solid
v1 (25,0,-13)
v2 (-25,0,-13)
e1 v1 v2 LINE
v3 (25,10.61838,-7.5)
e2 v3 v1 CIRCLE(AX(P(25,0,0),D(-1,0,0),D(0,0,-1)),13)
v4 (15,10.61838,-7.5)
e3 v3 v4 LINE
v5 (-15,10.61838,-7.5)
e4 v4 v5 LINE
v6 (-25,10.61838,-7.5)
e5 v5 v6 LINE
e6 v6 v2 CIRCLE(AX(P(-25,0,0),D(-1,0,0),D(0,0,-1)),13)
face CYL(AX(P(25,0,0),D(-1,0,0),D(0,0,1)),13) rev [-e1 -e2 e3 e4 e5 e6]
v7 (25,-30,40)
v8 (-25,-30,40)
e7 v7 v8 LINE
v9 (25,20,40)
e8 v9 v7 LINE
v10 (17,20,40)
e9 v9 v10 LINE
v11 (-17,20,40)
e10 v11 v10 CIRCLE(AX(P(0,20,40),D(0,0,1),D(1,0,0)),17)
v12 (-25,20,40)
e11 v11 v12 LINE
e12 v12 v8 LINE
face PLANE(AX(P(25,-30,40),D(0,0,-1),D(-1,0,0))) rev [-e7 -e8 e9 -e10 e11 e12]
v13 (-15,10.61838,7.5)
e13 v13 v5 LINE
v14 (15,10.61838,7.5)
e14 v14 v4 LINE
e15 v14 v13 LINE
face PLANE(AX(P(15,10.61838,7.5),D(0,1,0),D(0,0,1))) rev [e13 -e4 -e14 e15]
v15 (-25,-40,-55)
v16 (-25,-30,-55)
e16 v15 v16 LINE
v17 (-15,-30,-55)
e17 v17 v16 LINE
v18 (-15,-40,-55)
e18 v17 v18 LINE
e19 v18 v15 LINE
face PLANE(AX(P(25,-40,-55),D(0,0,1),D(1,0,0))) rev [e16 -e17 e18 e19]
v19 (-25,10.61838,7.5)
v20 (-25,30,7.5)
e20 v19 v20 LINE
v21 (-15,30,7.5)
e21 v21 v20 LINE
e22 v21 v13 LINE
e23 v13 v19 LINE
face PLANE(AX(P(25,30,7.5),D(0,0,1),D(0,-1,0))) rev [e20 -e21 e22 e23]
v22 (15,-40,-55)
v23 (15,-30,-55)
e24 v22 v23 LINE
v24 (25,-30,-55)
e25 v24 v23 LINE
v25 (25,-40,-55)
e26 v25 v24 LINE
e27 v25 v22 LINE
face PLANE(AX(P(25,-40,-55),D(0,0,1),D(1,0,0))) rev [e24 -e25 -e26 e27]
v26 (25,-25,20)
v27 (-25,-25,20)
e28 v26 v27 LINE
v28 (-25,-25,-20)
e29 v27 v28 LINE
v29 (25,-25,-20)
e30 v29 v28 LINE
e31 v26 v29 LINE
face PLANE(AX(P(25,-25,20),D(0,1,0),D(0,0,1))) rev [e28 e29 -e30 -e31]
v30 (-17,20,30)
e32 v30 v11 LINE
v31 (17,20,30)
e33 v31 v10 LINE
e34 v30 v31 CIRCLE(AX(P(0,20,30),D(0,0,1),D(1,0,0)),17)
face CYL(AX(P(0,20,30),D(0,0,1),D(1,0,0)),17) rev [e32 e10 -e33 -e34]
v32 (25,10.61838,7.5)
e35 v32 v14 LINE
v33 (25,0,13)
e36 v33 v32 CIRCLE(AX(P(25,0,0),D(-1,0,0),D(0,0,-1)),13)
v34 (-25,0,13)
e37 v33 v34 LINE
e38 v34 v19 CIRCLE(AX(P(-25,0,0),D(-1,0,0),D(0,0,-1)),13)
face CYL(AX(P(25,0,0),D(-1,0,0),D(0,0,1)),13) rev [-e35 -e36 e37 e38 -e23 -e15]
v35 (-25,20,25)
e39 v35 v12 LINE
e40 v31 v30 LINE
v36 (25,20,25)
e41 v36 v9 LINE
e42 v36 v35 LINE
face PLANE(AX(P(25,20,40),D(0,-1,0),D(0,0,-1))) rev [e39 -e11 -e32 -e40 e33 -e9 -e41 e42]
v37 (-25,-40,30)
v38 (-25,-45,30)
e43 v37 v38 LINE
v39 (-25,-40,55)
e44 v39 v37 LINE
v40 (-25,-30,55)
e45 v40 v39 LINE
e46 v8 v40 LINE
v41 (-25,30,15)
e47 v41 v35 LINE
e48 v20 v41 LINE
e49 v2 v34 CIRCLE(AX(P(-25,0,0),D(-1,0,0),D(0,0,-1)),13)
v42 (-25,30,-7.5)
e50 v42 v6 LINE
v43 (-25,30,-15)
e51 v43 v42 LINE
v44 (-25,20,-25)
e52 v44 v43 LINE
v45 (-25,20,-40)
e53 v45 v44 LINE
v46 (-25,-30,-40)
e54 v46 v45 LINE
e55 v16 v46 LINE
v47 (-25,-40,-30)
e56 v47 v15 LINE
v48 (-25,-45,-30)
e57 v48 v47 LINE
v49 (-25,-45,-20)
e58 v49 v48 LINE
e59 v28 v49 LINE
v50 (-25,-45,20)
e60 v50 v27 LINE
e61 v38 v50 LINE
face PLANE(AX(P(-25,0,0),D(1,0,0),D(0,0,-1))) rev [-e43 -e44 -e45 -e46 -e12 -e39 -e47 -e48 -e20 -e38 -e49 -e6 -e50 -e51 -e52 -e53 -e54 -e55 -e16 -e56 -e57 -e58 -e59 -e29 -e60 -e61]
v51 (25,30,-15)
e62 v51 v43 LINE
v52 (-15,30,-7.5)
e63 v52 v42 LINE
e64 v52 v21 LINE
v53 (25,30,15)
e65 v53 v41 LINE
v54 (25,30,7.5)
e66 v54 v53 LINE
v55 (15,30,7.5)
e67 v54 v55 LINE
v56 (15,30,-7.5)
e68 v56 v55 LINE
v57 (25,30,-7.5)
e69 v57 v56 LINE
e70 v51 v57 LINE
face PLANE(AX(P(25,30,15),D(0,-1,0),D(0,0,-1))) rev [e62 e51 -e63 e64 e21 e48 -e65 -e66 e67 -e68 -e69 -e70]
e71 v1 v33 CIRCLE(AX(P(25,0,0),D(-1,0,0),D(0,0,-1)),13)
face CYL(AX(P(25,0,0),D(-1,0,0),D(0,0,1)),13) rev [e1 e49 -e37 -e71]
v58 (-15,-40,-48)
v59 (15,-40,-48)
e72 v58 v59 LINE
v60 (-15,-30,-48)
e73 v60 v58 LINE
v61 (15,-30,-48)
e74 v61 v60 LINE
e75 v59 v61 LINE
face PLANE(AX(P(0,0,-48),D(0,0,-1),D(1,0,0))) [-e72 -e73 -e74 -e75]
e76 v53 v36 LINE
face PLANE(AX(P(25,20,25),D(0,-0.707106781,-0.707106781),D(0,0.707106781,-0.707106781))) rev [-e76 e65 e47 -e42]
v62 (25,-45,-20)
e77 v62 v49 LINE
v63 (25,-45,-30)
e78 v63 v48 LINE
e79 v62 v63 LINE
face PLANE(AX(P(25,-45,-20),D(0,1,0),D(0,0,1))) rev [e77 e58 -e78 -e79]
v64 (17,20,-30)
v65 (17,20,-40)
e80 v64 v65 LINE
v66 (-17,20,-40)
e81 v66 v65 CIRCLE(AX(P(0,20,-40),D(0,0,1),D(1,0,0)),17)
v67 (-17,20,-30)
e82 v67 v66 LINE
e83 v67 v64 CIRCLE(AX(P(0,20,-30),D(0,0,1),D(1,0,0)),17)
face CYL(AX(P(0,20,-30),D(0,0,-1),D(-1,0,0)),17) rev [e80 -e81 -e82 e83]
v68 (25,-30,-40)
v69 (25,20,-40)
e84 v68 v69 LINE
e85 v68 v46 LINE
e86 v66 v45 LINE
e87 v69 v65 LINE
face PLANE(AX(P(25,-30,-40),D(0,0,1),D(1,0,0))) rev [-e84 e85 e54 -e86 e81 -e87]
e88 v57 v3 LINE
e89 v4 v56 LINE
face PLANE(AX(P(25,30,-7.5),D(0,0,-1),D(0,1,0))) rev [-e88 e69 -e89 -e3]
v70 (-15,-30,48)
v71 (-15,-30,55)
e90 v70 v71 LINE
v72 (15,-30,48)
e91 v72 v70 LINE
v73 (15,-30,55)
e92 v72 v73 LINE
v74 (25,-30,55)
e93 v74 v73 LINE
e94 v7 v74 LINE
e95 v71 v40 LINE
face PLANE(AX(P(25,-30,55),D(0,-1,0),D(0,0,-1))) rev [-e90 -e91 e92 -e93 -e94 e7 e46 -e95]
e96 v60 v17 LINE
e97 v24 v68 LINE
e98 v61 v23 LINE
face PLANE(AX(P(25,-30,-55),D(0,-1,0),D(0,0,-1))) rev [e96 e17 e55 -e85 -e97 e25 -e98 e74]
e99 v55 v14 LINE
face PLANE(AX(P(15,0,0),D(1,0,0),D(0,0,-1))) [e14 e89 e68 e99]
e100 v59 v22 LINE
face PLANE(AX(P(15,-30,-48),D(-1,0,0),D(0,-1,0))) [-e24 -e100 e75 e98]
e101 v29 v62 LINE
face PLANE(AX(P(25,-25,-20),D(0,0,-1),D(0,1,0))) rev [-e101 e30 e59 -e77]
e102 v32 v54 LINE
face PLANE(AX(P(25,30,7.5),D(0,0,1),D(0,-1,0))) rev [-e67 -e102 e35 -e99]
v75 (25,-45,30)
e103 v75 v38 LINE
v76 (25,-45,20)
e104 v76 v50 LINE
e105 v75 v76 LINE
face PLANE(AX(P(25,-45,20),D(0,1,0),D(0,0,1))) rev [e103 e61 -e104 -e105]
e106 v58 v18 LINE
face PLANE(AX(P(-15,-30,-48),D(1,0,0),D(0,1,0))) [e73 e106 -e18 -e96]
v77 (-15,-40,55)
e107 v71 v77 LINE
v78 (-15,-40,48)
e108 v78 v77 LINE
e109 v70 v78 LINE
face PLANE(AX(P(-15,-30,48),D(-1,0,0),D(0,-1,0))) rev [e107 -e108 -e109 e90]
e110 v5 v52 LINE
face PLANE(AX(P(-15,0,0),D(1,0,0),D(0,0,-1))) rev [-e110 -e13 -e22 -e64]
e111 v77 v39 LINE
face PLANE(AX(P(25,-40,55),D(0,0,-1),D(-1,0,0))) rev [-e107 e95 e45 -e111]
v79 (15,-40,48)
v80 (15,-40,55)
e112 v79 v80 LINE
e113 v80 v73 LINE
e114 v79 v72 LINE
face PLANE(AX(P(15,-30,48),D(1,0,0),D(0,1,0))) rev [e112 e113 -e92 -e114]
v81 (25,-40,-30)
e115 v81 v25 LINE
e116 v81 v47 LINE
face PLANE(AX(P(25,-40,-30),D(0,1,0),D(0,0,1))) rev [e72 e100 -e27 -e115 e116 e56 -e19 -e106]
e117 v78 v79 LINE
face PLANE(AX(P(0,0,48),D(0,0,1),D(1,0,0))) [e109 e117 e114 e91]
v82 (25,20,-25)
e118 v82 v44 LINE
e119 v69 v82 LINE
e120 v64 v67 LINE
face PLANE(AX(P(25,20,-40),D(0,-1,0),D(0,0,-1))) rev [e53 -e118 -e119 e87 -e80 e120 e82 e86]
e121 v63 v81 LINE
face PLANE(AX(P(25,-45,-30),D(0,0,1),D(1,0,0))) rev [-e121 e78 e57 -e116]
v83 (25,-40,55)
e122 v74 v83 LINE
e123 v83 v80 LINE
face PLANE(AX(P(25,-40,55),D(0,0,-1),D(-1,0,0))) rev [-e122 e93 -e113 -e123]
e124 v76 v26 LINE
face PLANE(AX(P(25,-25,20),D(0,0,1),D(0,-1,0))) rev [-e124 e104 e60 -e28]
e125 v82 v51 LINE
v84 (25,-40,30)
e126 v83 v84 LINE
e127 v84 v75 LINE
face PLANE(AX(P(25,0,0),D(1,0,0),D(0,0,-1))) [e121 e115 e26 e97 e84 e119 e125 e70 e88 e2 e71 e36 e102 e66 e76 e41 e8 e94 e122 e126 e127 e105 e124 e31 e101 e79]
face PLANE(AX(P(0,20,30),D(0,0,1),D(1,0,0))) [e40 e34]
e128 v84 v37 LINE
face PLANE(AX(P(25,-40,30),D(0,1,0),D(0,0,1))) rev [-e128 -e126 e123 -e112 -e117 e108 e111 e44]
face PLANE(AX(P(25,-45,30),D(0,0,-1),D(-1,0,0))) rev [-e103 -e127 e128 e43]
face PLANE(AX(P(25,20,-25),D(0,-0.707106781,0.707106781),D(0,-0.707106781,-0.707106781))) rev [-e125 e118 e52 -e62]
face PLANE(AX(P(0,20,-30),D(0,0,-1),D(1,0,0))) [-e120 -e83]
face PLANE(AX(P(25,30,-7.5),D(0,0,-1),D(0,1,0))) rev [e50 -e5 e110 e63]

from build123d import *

# Parameters (mm, degrees)
STEPPED_BLOCK_BODY_50MM_DEPTH = 25
END_SLOT_PROFILE_30MM_W       = 30
END_SLOT_PROFILE_30MM_H       = 10
END_SLOT_CUT_7_DEEP_DEPTH     = 7
HALF_BORE_CUT_10_DEEP_DEPTH   = 10
CENTRE_BOSS_PROFILE_W         = 15
CENTRE_BOSS_PROFILE_H         = 19.381619709
CENTRE_BOSS_30MM_DEPTH        = 15


with BuildPart() as part:
    # Stepped Block Profile → Stepped Block Body 50mm (new, symmetric)
    with BuildSketch(Plane(origin=(0, 0, 0), x_dir=(0, 0, -1), z_dir=(1, 0, 0))):
        with BuildLine():
            Line((-20, -25), (20, -25))
            Line((20, -25), (20, -45))
            Line((20, -45), (30, -45))
            Line((30, -45), (30, -40))
            Line((30, -40), (55, -40))
            Line((55, -40), (55, -30))
            Line((55, -30), (40, -30))
            Line((40, -30), (40, 20))
            Line((40, 20), (25, 20))
            Line((25, 20), (15, 30))
            Line((15, 30), (7.5, 30))
            Line((7.5, 30), (7.5, 10.618380291))
            ThreePointArc((7.5, 10.618380291), (0, -13), (-7.5, 10.618380291))
            Line((-7.5, 10.618380291), (-7.5, 30))
            Line((-7.5, 30), (-15, 30))
            Line((-15, 30), (-25, 20))
            Line((-25, 20), (-40, 20))
            Line((-40, 20), (-40, -30))
            Line((-40, -30), (-55, -30))
            Line((-55, -30), (-55, -40))
            Line((-55, -40), (-30, -40))
            Line((-30, -40), (-30, -45))
            Line((-30, -45), (-20, -45))
            Line((-20, -45), (-20, -25))
        make_face()
    extrude(amount=STEPPED_BLOCK_BODY_50MM_DEPTH, both=True)

    # End Slot Profile 30mm → End Slot Cut 7 Deep (cut)
    with BuildSketch(Plane.XY.offset(55)):
        with Locations((0, -35)):
            Rectangle(END_SLOT_PROFILE_30MM_W, END_SLOT_PROFILE_30MM_H)
    end_slot_cut_7_deep = extrude(amount=-END_SLOT_CUT_7_DEEP_DEPTH, mode=Mode.SUBTRACT)

    # Half Bore Profile → Half Bore Cut 10 Deep (cut)
    with BuildSketch(Plane.XY.offset(40)):
        with BuildLine():
            Line((-17, 20), (17, 20))
            ThreePointArc((17, 20), (0, 3), (-17, 20))
        make_face()
    half_bore_cut_10_deep = extrude(amount=-HALF_BORE_CUT_10_DEEP_DEPTH, mode=Mode.SUBTRACT)

    # End Slot and Bore Mirror: End Slot Cut 7 Deep, Half Bore Cut 10 Deep across plane
    add(end_slot_cut_7_deep.mirror(Plane.XY), mode=Mode.SUBTRACT)
    add(half_bore_cut_10_deep.mirror(Plane.XY), mode=Mode.SUBTRACT)

    # Centre Boss Profile → Centre Boss 30mm (add, symmetric)
    with BuildSketch(Plane(origin=(0, 0, 0), x_dir=(0, 0, -1), z_dir=(1, 0, 0))):
        with Locations((0, 20.309190146)):
            Rectangle(CENTRE_BOSS_PROFILE_W, CENTRE_BOSS_PROFILE_H)
    extrude(amount=CENTRE_BOSS_30MM_DEPTH, both=True)


solid = part.part
